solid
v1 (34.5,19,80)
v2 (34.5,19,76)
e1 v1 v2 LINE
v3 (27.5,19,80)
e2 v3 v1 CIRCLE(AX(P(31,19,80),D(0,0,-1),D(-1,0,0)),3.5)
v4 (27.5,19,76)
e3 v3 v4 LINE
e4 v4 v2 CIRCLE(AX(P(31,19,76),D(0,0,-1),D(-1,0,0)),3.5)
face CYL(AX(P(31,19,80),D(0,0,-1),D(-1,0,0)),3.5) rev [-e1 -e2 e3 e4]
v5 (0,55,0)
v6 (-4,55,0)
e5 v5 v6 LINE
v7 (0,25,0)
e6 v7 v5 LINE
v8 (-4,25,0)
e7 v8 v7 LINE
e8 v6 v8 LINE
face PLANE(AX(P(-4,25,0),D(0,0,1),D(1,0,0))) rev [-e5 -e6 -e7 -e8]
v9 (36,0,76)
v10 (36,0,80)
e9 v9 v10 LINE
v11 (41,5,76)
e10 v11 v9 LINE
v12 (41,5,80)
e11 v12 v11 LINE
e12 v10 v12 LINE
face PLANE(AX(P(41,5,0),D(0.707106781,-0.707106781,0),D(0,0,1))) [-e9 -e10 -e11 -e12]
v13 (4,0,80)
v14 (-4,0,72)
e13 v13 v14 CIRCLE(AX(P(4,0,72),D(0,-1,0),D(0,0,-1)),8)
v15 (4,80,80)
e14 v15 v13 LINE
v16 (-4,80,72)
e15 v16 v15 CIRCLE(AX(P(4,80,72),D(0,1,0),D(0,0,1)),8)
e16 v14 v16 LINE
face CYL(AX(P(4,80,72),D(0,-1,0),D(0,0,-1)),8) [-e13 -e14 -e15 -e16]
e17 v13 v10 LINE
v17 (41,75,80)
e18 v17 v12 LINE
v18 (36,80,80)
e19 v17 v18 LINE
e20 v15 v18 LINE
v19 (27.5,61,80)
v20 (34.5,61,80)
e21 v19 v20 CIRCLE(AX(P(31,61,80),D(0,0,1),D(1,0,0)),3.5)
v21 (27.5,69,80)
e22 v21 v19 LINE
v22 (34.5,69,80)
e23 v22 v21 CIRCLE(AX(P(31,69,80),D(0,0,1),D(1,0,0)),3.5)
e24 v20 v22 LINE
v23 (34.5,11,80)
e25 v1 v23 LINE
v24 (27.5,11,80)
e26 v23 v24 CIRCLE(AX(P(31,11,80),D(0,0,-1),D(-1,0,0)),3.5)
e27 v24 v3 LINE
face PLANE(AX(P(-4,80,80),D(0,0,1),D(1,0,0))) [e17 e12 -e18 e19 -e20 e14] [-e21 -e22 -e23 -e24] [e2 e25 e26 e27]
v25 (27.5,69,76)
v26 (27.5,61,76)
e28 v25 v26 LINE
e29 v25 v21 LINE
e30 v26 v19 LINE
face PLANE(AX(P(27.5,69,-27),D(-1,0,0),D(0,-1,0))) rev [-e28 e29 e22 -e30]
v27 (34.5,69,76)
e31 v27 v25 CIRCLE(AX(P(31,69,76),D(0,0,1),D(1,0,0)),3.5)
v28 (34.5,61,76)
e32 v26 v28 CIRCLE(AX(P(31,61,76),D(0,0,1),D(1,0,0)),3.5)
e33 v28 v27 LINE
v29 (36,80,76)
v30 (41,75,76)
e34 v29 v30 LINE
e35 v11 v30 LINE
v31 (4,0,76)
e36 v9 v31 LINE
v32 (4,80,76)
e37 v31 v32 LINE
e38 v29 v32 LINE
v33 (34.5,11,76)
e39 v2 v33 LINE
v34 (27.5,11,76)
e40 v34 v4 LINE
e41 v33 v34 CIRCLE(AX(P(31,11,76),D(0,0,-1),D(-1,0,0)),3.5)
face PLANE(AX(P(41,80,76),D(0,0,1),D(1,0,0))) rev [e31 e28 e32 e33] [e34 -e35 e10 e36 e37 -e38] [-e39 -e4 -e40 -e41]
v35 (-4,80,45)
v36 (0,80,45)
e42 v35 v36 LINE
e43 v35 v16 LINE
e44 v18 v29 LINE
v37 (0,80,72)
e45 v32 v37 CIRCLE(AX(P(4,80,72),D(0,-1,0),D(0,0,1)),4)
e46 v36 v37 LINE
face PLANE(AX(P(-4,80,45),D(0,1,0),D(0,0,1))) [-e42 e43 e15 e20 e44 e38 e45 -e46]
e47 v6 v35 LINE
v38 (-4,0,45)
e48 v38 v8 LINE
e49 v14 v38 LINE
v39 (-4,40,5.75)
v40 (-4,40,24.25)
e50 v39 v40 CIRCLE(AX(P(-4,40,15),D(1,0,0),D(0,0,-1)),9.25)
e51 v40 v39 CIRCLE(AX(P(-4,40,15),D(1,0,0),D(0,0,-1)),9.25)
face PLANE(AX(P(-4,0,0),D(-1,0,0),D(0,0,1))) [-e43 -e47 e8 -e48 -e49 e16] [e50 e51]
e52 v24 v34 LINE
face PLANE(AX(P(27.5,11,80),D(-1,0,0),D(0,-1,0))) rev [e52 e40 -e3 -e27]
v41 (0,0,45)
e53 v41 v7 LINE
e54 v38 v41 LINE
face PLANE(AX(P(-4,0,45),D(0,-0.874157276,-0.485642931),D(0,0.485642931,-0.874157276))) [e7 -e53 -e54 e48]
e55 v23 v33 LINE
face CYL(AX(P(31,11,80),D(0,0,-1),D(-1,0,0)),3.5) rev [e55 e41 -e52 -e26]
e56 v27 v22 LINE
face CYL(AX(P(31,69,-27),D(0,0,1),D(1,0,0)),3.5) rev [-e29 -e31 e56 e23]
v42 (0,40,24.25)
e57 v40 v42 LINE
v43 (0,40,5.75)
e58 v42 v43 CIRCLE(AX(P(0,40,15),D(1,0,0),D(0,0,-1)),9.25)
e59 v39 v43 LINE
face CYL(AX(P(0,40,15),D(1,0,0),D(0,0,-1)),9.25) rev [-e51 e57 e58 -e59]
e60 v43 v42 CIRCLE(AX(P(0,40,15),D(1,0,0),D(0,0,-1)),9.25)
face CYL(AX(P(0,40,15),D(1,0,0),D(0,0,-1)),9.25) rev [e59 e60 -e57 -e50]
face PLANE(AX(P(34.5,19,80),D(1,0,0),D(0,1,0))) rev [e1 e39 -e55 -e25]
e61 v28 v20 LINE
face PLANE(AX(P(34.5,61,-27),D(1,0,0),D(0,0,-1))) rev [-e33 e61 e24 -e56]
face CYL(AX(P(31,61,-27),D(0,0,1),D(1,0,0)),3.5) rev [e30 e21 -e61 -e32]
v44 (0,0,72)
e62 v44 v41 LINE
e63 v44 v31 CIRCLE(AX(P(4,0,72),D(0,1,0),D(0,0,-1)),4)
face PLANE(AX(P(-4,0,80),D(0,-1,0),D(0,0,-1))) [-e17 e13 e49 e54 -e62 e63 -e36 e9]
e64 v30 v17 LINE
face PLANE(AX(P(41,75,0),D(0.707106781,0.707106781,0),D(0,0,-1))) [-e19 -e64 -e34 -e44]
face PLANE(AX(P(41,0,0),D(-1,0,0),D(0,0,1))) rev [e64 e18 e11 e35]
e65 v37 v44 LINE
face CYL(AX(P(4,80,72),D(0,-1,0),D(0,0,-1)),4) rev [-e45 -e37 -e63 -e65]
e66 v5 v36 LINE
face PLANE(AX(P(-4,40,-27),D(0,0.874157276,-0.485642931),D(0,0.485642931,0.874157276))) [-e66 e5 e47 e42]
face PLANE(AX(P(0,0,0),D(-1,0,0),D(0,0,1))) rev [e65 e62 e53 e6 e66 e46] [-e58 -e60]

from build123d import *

# Parameters (mm, degrees)
EXTRUDE_1_DEPTH           = 4
SKETCH_2_W                = 4
SKETCH_2_H                = 80
EXTRUDE_2_DEPTH           = 41
CUT_EXTRUDE_1_DEPTH       = 140.749776386
CUT_EXTRUDE_2_DEPTH       = 137.711374801
HOLE_WIZARD_18_5_18_5_1_D = 18.5
CHAMFER_1_SIZE            = 5
CHAMFER_2_SIZE            = 30.886890423
FILLET_1_R                = 4
FILLET_2_R                = 8


with BuildPart() as part:
    # 草图1 → 凸台-拉伸1 (new body)
    with BuildSketch(Plane(origin=(0, 0, 0), x_dir=(0, 0, -1), z_dir=(1, 0, 0))):
        Polygon((-45, 0), (27, 40), (-45, 80), (-80, 80), (-80, 0), align=None)
    extrude(amount=-EXTRUDE_1_DEPTH)

    # 草图2 → 凸台-拉伸2 (add)
    with BuildSketch(Plane(origin=(0, 0, 0), x_dir=(0, 0, -1), z_dir=(1, 0, 0))):
        with Locations((-78, 40)):
            Rectangle(SKETCH_2_W, SKETCH_2_H)
    extrude(amount=EXTRUDE_2_DEPTH)

    # 草图3 → 切除-拉伸1 (cut, through all)
    with BuildSketch(Plane.XY.offset(80)):
        with BuildLine():
            Line((34.5, 61), (34.5, 69))
            ThreePointArc((34.5, 69), (31, 72.5), (27.5, 69))
            Line((27.5, 69), (27.5, 61))
            ThreePointArc((27.5, 61), (31, 57.5), (34.5, 61))
        make_face()
    extrude(amount=-CUT_EXTRUDE_1_DEPTH, mode=Mode.SUBTRACT)

    # 草图4 → 切除-拉伸2 (cut, through all)
    with BuildSketch(Plane(origin=(0, 0, 76), x_dir=(-1, 0, 0), z_dir=(0, 0, -1))):
        with BuildLine():
            Line((-34.5, 19), (-34.5, 11))
            ThreePointArc((-34.5, 11), (-31, 7.5), (-27.5, 11))
            Line((-27.5, 11), (-27.5, 19))
            ThreePointArc((-27.5, 19), (-31, 22.5), (-34.5, 19))
        make_face()
    extrude(amount=-CUT_EXTRUDE_2_DEPTH, mode=Mode.SUBTRACT)

    # Ø18.5 (18.5) 直径孔1 (through all)
    with Locations(Plane(origin=(0, 0, 0), x_dir=(0, 0, -1), z_dir=(1, 0, 0))):
        with Locations((-15, 40)):
            Hole(HOLE_WIZARD_18_5_18_5_1_D / 2)

    # 倒角1
    chamfer_1_edges = [part.edges().sort_by_distance(p)[0] for p in [
        (41, 0, 78),
        (41, 80, 78),
    ]]
    chamfer(chamfer_1_edges, length=CHAMFER_1_SIZE)

    # 倒角2
    chamfer_2_edges = [part.edges().sort_by_distance(p)[0] for p in [
        (-2, 40, -27),
    ]]
    chamfer(chamfer_2_edges, length=CHAMFER_2_SIZE)

    # 圆角1
    fillet_1_edges = [part.edges().sort_by_distance(p)[0] for p in [
        (0, 40, 76),
    ]]
    fillet(fillet_1_edges, radius=FILLET_1_R)

    # 圆角2
    fillet_2_edges = [part.edges().sort_by_distance(p)[0] for p in [
        (-4, 40, 80),
    ]]
    fillet(fillet_2_edges, radius=FILLET_2_R)


solid = part.part
